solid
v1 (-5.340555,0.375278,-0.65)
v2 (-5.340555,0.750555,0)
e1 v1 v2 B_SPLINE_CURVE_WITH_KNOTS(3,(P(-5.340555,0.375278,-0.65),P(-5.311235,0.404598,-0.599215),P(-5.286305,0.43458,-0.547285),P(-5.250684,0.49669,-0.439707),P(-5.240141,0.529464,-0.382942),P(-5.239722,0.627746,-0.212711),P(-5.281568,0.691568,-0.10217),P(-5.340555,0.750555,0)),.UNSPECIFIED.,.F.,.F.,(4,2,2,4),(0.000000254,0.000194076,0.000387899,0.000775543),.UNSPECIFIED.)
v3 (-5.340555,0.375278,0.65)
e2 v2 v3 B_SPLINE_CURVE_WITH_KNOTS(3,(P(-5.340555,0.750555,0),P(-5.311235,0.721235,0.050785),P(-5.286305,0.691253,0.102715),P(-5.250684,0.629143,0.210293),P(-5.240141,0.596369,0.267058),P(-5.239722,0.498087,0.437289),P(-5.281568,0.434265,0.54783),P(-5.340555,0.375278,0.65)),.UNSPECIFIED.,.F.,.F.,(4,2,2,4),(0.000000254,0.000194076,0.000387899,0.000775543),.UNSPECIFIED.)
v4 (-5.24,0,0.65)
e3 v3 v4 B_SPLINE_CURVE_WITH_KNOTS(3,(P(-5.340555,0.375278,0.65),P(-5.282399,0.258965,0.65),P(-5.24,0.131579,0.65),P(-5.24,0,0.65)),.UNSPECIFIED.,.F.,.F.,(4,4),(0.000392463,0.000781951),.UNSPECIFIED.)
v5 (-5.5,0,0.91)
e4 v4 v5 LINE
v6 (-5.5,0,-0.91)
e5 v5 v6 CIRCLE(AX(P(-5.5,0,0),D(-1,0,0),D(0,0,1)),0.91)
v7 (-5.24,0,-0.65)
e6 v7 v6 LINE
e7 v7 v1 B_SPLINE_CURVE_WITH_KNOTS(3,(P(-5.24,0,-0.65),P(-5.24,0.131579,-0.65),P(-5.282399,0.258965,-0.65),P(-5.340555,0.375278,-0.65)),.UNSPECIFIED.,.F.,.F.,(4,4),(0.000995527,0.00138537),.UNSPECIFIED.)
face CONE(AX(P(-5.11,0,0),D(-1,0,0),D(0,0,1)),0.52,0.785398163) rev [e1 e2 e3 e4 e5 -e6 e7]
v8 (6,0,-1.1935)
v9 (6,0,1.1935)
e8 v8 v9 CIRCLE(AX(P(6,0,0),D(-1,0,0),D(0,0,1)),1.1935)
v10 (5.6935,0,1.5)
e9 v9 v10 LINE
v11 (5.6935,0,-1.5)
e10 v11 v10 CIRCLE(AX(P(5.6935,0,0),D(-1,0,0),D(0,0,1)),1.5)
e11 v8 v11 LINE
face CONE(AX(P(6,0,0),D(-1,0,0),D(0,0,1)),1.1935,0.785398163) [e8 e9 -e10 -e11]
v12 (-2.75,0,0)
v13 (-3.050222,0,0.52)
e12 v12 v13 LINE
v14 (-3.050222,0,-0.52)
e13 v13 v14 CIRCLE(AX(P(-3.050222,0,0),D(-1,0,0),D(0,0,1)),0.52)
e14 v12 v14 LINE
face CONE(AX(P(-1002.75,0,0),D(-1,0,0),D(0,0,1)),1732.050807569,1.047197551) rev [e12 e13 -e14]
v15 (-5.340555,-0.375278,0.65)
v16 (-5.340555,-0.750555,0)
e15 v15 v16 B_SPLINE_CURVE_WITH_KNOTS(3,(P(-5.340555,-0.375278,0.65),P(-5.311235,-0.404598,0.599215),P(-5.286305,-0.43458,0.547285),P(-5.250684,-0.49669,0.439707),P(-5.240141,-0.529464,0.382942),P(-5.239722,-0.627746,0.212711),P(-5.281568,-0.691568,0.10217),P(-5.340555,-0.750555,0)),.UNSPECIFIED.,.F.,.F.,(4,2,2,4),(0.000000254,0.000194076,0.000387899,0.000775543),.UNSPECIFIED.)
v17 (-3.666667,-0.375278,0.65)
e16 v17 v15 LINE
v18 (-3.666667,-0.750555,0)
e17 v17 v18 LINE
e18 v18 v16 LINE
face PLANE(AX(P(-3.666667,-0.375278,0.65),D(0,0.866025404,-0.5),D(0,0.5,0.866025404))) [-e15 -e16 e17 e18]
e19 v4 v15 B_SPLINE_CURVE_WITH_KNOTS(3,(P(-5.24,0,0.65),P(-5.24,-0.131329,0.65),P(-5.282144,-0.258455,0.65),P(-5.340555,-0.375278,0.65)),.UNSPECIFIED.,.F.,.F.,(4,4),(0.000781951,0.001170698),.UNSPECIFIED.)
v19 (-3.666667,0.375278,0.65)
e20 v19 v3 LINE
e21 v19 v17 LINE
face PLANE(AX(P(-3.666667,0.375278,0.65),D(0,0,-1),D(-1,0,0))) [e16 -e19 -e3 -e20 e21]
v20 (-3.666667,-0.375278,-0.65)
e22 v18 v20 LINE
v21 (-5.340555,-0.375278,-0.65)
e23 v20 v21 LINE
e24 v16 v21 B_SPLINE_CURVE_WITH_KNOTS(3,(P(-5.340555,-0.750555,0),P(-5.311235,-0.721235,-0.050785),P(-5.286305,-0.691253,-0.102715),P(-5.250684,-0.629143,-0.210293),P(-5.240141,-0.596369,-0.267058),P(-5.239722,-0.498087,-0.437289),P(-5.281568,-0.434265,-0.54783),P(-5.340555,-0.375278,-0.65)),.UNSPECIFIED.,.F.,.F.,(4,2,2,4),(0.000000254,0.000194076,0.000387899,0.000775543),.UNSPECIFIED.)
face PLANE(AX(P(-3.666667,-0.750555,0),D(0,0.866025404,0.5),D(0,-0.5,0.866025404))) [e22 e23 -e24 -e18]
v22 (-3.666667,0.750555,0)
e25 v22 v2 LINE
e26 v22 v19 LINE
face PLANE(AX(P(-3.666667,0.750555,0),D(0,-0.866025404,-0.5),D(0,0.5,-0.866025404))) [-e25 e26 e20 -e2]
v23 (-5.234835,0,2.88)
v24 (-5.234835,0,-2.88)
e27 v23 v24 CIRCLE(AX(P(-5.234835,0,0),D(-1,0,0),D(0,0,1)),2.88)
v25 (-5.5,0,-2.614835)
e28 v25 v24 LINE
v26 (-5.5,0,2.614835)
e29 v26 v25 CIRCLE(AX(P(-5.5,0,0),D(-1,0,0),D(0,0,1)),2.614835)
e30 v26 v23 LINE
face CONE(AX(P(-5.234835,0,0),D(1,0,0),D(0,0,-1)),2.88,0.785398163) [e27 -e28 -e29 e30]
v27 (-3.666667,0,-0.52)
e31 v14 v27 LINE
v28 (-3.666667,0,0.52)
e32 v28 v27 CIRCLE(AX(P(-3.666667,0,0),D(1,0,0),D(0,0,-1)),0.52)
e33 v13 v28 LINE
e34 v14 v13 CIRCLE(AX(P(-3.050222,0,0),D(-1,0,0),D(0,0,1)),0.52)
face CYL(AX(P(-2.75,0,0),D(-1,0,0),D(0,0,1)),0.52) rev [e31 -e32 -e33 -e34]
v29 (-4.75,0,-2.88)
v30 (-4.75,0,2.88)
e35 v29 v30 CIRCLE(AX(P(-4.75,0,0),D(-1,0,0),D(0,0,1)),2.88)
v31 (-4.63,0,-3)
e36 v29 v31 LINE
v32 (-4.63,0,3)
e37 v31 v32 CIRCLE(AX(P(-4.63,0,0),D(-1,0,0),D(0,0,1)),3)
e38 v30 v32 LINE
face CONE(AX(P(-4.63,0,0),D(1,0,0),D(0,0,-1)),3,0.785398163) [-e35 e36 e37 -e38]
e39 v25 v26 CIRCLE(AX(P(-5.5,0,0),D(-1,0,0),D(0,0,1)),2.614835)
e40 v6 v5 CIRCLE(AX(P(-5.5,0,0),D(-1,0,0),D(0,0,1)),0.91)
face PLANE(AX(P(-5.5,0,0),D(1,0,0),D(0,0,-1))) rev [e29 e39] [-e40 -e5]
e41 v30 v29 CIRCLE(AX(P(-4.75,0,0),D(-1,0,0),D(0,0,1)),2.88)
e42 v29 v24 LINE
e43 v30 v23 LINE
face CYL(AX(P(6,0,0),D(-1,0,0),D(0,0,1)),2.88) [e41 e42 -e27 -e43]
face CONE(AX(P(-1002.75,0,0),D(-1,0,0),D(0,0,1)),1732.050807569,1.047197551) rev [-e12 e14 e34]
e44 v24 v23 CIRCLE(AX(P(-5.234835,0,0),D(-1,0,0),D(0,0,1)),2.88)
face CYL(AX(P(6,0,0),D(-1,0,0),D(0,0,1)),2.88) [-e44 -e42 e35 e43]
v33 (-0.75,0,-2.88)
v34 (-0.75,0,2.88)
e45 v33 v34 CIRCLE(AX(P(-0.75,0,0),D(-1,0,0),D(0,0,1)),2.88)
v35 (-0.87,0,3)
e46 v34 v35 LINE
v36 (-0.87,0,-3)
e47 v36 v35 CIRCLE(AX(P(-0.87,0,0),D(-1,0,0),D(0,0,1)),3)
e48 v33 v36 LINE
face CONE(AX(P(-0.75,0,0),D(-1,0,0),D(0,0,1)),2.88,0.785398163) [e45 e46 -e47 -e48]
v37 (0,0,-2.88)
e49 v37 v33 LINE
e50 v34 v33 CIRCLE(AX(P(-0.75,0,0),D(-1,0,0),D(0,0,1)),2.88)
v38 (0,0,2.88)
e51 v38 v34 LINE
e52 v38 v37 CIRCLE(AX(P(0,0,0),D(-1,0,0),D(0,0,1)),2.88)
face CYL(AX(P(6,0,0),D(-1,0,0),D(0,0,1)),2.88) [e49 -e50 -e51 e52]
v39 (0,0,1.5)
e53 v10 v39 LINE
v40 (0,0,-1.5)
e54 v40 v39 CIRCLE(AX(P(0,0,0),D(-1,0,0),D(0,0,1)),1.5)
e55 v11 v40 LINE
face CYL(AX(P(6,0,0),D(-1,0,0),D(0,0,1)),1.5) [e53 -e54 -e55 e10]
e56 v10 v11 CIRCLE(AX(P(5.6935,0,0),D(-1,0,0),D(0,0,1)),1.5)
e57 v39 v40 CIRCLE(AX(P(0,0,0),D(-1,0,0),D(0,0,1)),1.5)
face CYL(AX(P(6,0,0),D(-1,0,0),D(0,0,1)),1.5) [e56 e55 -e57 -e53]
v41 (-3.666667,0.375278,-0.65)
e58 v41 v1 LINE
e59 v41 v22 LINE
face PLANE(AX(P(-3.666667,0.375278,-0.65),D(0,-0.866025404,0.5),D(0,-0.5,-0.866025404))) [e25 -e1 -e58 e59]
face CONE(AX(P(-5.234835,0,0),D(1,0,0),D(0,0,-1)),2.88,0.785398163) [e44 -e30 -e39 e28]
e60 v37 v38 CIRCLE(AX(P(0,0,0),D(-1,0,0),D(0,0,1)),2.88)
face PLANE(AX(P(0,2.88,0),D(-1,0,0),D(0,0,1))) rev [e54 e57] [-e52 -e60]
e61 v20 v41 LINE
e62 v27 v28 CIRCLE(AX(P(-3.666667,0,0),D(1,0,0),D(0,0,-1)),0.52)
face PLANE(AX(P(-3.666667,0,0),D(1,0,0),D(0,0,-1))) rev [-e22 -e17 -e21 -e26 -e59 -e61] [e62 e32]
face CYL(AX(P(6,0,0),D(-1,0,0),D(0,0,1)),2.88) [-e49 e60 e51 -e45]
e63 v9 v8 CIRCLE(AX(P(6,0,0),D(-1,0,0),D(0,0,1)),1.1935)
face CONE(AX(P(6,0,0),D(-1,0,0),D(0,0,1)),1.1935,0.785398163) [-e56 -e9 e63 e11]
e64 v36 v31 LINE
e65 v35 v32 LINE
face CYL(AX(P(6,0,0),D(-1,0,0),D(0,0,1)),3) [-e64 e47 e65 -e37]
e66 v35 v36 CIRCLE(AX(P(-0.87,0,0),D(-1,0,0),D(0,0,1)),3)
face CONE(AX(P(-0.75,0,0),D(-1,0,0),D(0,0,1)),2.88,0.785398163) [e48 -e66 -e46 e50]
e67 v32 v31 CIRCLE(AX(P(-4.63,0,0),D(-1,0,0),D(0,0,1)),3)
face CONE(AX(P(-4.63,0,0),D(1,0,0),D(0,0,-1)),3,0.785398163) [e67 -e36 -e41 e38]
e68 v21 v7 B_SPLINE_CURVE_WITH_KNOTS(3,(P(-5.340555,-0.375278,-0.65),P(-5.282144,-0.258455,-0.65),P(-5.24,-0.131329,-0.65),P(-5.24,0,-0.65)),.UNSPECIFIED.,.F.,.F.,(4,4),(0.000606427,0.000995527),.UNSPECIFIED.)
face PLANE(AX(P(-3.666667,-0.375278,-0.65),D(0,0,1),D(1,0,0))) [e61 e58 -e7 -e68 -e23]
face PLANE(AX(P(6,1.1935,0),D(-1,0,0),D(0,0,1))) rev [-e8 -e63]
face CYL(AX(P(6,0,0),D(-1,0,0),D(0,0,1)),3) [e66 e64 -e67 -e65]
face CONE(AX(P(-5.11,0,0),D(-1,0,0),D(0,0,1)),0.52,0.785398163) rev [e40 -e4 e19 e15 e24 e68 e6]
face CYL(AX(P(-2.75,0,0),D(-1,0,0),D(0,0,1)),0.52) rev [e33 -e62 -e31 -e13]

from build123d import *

# Parameters (mm, degrees)
CUT_EXTRUDE1_DEPTH = 1.833333333


with BuildPart() as part:
    # Sketch1 → Revolve1 (revolve)
    with BuildSketch(Plane.XY, mode=Mode.PRIVATE) as revolve1_sk:
        Polygon((-5.5, 0), (-5.5, 2.614834957), (-5.234834957, 2.88), (-4.75, 2.88), (-4.63, 3), (-0.87, 3), (-0.75, 2.88), (0, 2.88), (0, 1.5), (5.6935, 1.5), (6, 1.1935), (6, 0), align=None)
    revolve(revolve1_sk.sketch.rotate(Axis((6, 0, 0), (-1, 0, 0)), 270), axis=Axis((6, 0, 0), (-1, 0, 0)))

    # Sketch2 → Cut-Revolve1 (revolve, cut)
    with BuildSketch(Plane.XY, mode=Mode.PRIVATE) as cut_revolve1_sk:
        Polygon((-5.5, 0), (-5.5, 0.91), (-5.11, 0.52), (-3.05022214, 0.52), (-2.75, 0), align=None)
    revolve(cut_revolve1_sk.sketch.rotate(Axis((-2.75, 0, 0), (-1, 0, 0)), 270), axis=Axis((-2.75, 0, 0), (-1, 0, 0)), mode=Mode.SUBTRACT)

    # Sketch3 → Cut-Extrude1 (cut)
    with BuildSketch(Plane(origin=(-5.5, 0, 0), x_dir=(0, 0, -1), z_dir=(1, 0, 0))):
        Polygon((-0.65, 0.375277675), (-0.65, -0.375277675), (0, -0.75055535), (0.65, -0.375277675), (0.65, 0.375277675), (0, 0.75055535), align=None)
    extrude(amount=CUT_EXTRUDE1_DEPTH, mode=Mode.SUBTRACT)


solid = part.part
